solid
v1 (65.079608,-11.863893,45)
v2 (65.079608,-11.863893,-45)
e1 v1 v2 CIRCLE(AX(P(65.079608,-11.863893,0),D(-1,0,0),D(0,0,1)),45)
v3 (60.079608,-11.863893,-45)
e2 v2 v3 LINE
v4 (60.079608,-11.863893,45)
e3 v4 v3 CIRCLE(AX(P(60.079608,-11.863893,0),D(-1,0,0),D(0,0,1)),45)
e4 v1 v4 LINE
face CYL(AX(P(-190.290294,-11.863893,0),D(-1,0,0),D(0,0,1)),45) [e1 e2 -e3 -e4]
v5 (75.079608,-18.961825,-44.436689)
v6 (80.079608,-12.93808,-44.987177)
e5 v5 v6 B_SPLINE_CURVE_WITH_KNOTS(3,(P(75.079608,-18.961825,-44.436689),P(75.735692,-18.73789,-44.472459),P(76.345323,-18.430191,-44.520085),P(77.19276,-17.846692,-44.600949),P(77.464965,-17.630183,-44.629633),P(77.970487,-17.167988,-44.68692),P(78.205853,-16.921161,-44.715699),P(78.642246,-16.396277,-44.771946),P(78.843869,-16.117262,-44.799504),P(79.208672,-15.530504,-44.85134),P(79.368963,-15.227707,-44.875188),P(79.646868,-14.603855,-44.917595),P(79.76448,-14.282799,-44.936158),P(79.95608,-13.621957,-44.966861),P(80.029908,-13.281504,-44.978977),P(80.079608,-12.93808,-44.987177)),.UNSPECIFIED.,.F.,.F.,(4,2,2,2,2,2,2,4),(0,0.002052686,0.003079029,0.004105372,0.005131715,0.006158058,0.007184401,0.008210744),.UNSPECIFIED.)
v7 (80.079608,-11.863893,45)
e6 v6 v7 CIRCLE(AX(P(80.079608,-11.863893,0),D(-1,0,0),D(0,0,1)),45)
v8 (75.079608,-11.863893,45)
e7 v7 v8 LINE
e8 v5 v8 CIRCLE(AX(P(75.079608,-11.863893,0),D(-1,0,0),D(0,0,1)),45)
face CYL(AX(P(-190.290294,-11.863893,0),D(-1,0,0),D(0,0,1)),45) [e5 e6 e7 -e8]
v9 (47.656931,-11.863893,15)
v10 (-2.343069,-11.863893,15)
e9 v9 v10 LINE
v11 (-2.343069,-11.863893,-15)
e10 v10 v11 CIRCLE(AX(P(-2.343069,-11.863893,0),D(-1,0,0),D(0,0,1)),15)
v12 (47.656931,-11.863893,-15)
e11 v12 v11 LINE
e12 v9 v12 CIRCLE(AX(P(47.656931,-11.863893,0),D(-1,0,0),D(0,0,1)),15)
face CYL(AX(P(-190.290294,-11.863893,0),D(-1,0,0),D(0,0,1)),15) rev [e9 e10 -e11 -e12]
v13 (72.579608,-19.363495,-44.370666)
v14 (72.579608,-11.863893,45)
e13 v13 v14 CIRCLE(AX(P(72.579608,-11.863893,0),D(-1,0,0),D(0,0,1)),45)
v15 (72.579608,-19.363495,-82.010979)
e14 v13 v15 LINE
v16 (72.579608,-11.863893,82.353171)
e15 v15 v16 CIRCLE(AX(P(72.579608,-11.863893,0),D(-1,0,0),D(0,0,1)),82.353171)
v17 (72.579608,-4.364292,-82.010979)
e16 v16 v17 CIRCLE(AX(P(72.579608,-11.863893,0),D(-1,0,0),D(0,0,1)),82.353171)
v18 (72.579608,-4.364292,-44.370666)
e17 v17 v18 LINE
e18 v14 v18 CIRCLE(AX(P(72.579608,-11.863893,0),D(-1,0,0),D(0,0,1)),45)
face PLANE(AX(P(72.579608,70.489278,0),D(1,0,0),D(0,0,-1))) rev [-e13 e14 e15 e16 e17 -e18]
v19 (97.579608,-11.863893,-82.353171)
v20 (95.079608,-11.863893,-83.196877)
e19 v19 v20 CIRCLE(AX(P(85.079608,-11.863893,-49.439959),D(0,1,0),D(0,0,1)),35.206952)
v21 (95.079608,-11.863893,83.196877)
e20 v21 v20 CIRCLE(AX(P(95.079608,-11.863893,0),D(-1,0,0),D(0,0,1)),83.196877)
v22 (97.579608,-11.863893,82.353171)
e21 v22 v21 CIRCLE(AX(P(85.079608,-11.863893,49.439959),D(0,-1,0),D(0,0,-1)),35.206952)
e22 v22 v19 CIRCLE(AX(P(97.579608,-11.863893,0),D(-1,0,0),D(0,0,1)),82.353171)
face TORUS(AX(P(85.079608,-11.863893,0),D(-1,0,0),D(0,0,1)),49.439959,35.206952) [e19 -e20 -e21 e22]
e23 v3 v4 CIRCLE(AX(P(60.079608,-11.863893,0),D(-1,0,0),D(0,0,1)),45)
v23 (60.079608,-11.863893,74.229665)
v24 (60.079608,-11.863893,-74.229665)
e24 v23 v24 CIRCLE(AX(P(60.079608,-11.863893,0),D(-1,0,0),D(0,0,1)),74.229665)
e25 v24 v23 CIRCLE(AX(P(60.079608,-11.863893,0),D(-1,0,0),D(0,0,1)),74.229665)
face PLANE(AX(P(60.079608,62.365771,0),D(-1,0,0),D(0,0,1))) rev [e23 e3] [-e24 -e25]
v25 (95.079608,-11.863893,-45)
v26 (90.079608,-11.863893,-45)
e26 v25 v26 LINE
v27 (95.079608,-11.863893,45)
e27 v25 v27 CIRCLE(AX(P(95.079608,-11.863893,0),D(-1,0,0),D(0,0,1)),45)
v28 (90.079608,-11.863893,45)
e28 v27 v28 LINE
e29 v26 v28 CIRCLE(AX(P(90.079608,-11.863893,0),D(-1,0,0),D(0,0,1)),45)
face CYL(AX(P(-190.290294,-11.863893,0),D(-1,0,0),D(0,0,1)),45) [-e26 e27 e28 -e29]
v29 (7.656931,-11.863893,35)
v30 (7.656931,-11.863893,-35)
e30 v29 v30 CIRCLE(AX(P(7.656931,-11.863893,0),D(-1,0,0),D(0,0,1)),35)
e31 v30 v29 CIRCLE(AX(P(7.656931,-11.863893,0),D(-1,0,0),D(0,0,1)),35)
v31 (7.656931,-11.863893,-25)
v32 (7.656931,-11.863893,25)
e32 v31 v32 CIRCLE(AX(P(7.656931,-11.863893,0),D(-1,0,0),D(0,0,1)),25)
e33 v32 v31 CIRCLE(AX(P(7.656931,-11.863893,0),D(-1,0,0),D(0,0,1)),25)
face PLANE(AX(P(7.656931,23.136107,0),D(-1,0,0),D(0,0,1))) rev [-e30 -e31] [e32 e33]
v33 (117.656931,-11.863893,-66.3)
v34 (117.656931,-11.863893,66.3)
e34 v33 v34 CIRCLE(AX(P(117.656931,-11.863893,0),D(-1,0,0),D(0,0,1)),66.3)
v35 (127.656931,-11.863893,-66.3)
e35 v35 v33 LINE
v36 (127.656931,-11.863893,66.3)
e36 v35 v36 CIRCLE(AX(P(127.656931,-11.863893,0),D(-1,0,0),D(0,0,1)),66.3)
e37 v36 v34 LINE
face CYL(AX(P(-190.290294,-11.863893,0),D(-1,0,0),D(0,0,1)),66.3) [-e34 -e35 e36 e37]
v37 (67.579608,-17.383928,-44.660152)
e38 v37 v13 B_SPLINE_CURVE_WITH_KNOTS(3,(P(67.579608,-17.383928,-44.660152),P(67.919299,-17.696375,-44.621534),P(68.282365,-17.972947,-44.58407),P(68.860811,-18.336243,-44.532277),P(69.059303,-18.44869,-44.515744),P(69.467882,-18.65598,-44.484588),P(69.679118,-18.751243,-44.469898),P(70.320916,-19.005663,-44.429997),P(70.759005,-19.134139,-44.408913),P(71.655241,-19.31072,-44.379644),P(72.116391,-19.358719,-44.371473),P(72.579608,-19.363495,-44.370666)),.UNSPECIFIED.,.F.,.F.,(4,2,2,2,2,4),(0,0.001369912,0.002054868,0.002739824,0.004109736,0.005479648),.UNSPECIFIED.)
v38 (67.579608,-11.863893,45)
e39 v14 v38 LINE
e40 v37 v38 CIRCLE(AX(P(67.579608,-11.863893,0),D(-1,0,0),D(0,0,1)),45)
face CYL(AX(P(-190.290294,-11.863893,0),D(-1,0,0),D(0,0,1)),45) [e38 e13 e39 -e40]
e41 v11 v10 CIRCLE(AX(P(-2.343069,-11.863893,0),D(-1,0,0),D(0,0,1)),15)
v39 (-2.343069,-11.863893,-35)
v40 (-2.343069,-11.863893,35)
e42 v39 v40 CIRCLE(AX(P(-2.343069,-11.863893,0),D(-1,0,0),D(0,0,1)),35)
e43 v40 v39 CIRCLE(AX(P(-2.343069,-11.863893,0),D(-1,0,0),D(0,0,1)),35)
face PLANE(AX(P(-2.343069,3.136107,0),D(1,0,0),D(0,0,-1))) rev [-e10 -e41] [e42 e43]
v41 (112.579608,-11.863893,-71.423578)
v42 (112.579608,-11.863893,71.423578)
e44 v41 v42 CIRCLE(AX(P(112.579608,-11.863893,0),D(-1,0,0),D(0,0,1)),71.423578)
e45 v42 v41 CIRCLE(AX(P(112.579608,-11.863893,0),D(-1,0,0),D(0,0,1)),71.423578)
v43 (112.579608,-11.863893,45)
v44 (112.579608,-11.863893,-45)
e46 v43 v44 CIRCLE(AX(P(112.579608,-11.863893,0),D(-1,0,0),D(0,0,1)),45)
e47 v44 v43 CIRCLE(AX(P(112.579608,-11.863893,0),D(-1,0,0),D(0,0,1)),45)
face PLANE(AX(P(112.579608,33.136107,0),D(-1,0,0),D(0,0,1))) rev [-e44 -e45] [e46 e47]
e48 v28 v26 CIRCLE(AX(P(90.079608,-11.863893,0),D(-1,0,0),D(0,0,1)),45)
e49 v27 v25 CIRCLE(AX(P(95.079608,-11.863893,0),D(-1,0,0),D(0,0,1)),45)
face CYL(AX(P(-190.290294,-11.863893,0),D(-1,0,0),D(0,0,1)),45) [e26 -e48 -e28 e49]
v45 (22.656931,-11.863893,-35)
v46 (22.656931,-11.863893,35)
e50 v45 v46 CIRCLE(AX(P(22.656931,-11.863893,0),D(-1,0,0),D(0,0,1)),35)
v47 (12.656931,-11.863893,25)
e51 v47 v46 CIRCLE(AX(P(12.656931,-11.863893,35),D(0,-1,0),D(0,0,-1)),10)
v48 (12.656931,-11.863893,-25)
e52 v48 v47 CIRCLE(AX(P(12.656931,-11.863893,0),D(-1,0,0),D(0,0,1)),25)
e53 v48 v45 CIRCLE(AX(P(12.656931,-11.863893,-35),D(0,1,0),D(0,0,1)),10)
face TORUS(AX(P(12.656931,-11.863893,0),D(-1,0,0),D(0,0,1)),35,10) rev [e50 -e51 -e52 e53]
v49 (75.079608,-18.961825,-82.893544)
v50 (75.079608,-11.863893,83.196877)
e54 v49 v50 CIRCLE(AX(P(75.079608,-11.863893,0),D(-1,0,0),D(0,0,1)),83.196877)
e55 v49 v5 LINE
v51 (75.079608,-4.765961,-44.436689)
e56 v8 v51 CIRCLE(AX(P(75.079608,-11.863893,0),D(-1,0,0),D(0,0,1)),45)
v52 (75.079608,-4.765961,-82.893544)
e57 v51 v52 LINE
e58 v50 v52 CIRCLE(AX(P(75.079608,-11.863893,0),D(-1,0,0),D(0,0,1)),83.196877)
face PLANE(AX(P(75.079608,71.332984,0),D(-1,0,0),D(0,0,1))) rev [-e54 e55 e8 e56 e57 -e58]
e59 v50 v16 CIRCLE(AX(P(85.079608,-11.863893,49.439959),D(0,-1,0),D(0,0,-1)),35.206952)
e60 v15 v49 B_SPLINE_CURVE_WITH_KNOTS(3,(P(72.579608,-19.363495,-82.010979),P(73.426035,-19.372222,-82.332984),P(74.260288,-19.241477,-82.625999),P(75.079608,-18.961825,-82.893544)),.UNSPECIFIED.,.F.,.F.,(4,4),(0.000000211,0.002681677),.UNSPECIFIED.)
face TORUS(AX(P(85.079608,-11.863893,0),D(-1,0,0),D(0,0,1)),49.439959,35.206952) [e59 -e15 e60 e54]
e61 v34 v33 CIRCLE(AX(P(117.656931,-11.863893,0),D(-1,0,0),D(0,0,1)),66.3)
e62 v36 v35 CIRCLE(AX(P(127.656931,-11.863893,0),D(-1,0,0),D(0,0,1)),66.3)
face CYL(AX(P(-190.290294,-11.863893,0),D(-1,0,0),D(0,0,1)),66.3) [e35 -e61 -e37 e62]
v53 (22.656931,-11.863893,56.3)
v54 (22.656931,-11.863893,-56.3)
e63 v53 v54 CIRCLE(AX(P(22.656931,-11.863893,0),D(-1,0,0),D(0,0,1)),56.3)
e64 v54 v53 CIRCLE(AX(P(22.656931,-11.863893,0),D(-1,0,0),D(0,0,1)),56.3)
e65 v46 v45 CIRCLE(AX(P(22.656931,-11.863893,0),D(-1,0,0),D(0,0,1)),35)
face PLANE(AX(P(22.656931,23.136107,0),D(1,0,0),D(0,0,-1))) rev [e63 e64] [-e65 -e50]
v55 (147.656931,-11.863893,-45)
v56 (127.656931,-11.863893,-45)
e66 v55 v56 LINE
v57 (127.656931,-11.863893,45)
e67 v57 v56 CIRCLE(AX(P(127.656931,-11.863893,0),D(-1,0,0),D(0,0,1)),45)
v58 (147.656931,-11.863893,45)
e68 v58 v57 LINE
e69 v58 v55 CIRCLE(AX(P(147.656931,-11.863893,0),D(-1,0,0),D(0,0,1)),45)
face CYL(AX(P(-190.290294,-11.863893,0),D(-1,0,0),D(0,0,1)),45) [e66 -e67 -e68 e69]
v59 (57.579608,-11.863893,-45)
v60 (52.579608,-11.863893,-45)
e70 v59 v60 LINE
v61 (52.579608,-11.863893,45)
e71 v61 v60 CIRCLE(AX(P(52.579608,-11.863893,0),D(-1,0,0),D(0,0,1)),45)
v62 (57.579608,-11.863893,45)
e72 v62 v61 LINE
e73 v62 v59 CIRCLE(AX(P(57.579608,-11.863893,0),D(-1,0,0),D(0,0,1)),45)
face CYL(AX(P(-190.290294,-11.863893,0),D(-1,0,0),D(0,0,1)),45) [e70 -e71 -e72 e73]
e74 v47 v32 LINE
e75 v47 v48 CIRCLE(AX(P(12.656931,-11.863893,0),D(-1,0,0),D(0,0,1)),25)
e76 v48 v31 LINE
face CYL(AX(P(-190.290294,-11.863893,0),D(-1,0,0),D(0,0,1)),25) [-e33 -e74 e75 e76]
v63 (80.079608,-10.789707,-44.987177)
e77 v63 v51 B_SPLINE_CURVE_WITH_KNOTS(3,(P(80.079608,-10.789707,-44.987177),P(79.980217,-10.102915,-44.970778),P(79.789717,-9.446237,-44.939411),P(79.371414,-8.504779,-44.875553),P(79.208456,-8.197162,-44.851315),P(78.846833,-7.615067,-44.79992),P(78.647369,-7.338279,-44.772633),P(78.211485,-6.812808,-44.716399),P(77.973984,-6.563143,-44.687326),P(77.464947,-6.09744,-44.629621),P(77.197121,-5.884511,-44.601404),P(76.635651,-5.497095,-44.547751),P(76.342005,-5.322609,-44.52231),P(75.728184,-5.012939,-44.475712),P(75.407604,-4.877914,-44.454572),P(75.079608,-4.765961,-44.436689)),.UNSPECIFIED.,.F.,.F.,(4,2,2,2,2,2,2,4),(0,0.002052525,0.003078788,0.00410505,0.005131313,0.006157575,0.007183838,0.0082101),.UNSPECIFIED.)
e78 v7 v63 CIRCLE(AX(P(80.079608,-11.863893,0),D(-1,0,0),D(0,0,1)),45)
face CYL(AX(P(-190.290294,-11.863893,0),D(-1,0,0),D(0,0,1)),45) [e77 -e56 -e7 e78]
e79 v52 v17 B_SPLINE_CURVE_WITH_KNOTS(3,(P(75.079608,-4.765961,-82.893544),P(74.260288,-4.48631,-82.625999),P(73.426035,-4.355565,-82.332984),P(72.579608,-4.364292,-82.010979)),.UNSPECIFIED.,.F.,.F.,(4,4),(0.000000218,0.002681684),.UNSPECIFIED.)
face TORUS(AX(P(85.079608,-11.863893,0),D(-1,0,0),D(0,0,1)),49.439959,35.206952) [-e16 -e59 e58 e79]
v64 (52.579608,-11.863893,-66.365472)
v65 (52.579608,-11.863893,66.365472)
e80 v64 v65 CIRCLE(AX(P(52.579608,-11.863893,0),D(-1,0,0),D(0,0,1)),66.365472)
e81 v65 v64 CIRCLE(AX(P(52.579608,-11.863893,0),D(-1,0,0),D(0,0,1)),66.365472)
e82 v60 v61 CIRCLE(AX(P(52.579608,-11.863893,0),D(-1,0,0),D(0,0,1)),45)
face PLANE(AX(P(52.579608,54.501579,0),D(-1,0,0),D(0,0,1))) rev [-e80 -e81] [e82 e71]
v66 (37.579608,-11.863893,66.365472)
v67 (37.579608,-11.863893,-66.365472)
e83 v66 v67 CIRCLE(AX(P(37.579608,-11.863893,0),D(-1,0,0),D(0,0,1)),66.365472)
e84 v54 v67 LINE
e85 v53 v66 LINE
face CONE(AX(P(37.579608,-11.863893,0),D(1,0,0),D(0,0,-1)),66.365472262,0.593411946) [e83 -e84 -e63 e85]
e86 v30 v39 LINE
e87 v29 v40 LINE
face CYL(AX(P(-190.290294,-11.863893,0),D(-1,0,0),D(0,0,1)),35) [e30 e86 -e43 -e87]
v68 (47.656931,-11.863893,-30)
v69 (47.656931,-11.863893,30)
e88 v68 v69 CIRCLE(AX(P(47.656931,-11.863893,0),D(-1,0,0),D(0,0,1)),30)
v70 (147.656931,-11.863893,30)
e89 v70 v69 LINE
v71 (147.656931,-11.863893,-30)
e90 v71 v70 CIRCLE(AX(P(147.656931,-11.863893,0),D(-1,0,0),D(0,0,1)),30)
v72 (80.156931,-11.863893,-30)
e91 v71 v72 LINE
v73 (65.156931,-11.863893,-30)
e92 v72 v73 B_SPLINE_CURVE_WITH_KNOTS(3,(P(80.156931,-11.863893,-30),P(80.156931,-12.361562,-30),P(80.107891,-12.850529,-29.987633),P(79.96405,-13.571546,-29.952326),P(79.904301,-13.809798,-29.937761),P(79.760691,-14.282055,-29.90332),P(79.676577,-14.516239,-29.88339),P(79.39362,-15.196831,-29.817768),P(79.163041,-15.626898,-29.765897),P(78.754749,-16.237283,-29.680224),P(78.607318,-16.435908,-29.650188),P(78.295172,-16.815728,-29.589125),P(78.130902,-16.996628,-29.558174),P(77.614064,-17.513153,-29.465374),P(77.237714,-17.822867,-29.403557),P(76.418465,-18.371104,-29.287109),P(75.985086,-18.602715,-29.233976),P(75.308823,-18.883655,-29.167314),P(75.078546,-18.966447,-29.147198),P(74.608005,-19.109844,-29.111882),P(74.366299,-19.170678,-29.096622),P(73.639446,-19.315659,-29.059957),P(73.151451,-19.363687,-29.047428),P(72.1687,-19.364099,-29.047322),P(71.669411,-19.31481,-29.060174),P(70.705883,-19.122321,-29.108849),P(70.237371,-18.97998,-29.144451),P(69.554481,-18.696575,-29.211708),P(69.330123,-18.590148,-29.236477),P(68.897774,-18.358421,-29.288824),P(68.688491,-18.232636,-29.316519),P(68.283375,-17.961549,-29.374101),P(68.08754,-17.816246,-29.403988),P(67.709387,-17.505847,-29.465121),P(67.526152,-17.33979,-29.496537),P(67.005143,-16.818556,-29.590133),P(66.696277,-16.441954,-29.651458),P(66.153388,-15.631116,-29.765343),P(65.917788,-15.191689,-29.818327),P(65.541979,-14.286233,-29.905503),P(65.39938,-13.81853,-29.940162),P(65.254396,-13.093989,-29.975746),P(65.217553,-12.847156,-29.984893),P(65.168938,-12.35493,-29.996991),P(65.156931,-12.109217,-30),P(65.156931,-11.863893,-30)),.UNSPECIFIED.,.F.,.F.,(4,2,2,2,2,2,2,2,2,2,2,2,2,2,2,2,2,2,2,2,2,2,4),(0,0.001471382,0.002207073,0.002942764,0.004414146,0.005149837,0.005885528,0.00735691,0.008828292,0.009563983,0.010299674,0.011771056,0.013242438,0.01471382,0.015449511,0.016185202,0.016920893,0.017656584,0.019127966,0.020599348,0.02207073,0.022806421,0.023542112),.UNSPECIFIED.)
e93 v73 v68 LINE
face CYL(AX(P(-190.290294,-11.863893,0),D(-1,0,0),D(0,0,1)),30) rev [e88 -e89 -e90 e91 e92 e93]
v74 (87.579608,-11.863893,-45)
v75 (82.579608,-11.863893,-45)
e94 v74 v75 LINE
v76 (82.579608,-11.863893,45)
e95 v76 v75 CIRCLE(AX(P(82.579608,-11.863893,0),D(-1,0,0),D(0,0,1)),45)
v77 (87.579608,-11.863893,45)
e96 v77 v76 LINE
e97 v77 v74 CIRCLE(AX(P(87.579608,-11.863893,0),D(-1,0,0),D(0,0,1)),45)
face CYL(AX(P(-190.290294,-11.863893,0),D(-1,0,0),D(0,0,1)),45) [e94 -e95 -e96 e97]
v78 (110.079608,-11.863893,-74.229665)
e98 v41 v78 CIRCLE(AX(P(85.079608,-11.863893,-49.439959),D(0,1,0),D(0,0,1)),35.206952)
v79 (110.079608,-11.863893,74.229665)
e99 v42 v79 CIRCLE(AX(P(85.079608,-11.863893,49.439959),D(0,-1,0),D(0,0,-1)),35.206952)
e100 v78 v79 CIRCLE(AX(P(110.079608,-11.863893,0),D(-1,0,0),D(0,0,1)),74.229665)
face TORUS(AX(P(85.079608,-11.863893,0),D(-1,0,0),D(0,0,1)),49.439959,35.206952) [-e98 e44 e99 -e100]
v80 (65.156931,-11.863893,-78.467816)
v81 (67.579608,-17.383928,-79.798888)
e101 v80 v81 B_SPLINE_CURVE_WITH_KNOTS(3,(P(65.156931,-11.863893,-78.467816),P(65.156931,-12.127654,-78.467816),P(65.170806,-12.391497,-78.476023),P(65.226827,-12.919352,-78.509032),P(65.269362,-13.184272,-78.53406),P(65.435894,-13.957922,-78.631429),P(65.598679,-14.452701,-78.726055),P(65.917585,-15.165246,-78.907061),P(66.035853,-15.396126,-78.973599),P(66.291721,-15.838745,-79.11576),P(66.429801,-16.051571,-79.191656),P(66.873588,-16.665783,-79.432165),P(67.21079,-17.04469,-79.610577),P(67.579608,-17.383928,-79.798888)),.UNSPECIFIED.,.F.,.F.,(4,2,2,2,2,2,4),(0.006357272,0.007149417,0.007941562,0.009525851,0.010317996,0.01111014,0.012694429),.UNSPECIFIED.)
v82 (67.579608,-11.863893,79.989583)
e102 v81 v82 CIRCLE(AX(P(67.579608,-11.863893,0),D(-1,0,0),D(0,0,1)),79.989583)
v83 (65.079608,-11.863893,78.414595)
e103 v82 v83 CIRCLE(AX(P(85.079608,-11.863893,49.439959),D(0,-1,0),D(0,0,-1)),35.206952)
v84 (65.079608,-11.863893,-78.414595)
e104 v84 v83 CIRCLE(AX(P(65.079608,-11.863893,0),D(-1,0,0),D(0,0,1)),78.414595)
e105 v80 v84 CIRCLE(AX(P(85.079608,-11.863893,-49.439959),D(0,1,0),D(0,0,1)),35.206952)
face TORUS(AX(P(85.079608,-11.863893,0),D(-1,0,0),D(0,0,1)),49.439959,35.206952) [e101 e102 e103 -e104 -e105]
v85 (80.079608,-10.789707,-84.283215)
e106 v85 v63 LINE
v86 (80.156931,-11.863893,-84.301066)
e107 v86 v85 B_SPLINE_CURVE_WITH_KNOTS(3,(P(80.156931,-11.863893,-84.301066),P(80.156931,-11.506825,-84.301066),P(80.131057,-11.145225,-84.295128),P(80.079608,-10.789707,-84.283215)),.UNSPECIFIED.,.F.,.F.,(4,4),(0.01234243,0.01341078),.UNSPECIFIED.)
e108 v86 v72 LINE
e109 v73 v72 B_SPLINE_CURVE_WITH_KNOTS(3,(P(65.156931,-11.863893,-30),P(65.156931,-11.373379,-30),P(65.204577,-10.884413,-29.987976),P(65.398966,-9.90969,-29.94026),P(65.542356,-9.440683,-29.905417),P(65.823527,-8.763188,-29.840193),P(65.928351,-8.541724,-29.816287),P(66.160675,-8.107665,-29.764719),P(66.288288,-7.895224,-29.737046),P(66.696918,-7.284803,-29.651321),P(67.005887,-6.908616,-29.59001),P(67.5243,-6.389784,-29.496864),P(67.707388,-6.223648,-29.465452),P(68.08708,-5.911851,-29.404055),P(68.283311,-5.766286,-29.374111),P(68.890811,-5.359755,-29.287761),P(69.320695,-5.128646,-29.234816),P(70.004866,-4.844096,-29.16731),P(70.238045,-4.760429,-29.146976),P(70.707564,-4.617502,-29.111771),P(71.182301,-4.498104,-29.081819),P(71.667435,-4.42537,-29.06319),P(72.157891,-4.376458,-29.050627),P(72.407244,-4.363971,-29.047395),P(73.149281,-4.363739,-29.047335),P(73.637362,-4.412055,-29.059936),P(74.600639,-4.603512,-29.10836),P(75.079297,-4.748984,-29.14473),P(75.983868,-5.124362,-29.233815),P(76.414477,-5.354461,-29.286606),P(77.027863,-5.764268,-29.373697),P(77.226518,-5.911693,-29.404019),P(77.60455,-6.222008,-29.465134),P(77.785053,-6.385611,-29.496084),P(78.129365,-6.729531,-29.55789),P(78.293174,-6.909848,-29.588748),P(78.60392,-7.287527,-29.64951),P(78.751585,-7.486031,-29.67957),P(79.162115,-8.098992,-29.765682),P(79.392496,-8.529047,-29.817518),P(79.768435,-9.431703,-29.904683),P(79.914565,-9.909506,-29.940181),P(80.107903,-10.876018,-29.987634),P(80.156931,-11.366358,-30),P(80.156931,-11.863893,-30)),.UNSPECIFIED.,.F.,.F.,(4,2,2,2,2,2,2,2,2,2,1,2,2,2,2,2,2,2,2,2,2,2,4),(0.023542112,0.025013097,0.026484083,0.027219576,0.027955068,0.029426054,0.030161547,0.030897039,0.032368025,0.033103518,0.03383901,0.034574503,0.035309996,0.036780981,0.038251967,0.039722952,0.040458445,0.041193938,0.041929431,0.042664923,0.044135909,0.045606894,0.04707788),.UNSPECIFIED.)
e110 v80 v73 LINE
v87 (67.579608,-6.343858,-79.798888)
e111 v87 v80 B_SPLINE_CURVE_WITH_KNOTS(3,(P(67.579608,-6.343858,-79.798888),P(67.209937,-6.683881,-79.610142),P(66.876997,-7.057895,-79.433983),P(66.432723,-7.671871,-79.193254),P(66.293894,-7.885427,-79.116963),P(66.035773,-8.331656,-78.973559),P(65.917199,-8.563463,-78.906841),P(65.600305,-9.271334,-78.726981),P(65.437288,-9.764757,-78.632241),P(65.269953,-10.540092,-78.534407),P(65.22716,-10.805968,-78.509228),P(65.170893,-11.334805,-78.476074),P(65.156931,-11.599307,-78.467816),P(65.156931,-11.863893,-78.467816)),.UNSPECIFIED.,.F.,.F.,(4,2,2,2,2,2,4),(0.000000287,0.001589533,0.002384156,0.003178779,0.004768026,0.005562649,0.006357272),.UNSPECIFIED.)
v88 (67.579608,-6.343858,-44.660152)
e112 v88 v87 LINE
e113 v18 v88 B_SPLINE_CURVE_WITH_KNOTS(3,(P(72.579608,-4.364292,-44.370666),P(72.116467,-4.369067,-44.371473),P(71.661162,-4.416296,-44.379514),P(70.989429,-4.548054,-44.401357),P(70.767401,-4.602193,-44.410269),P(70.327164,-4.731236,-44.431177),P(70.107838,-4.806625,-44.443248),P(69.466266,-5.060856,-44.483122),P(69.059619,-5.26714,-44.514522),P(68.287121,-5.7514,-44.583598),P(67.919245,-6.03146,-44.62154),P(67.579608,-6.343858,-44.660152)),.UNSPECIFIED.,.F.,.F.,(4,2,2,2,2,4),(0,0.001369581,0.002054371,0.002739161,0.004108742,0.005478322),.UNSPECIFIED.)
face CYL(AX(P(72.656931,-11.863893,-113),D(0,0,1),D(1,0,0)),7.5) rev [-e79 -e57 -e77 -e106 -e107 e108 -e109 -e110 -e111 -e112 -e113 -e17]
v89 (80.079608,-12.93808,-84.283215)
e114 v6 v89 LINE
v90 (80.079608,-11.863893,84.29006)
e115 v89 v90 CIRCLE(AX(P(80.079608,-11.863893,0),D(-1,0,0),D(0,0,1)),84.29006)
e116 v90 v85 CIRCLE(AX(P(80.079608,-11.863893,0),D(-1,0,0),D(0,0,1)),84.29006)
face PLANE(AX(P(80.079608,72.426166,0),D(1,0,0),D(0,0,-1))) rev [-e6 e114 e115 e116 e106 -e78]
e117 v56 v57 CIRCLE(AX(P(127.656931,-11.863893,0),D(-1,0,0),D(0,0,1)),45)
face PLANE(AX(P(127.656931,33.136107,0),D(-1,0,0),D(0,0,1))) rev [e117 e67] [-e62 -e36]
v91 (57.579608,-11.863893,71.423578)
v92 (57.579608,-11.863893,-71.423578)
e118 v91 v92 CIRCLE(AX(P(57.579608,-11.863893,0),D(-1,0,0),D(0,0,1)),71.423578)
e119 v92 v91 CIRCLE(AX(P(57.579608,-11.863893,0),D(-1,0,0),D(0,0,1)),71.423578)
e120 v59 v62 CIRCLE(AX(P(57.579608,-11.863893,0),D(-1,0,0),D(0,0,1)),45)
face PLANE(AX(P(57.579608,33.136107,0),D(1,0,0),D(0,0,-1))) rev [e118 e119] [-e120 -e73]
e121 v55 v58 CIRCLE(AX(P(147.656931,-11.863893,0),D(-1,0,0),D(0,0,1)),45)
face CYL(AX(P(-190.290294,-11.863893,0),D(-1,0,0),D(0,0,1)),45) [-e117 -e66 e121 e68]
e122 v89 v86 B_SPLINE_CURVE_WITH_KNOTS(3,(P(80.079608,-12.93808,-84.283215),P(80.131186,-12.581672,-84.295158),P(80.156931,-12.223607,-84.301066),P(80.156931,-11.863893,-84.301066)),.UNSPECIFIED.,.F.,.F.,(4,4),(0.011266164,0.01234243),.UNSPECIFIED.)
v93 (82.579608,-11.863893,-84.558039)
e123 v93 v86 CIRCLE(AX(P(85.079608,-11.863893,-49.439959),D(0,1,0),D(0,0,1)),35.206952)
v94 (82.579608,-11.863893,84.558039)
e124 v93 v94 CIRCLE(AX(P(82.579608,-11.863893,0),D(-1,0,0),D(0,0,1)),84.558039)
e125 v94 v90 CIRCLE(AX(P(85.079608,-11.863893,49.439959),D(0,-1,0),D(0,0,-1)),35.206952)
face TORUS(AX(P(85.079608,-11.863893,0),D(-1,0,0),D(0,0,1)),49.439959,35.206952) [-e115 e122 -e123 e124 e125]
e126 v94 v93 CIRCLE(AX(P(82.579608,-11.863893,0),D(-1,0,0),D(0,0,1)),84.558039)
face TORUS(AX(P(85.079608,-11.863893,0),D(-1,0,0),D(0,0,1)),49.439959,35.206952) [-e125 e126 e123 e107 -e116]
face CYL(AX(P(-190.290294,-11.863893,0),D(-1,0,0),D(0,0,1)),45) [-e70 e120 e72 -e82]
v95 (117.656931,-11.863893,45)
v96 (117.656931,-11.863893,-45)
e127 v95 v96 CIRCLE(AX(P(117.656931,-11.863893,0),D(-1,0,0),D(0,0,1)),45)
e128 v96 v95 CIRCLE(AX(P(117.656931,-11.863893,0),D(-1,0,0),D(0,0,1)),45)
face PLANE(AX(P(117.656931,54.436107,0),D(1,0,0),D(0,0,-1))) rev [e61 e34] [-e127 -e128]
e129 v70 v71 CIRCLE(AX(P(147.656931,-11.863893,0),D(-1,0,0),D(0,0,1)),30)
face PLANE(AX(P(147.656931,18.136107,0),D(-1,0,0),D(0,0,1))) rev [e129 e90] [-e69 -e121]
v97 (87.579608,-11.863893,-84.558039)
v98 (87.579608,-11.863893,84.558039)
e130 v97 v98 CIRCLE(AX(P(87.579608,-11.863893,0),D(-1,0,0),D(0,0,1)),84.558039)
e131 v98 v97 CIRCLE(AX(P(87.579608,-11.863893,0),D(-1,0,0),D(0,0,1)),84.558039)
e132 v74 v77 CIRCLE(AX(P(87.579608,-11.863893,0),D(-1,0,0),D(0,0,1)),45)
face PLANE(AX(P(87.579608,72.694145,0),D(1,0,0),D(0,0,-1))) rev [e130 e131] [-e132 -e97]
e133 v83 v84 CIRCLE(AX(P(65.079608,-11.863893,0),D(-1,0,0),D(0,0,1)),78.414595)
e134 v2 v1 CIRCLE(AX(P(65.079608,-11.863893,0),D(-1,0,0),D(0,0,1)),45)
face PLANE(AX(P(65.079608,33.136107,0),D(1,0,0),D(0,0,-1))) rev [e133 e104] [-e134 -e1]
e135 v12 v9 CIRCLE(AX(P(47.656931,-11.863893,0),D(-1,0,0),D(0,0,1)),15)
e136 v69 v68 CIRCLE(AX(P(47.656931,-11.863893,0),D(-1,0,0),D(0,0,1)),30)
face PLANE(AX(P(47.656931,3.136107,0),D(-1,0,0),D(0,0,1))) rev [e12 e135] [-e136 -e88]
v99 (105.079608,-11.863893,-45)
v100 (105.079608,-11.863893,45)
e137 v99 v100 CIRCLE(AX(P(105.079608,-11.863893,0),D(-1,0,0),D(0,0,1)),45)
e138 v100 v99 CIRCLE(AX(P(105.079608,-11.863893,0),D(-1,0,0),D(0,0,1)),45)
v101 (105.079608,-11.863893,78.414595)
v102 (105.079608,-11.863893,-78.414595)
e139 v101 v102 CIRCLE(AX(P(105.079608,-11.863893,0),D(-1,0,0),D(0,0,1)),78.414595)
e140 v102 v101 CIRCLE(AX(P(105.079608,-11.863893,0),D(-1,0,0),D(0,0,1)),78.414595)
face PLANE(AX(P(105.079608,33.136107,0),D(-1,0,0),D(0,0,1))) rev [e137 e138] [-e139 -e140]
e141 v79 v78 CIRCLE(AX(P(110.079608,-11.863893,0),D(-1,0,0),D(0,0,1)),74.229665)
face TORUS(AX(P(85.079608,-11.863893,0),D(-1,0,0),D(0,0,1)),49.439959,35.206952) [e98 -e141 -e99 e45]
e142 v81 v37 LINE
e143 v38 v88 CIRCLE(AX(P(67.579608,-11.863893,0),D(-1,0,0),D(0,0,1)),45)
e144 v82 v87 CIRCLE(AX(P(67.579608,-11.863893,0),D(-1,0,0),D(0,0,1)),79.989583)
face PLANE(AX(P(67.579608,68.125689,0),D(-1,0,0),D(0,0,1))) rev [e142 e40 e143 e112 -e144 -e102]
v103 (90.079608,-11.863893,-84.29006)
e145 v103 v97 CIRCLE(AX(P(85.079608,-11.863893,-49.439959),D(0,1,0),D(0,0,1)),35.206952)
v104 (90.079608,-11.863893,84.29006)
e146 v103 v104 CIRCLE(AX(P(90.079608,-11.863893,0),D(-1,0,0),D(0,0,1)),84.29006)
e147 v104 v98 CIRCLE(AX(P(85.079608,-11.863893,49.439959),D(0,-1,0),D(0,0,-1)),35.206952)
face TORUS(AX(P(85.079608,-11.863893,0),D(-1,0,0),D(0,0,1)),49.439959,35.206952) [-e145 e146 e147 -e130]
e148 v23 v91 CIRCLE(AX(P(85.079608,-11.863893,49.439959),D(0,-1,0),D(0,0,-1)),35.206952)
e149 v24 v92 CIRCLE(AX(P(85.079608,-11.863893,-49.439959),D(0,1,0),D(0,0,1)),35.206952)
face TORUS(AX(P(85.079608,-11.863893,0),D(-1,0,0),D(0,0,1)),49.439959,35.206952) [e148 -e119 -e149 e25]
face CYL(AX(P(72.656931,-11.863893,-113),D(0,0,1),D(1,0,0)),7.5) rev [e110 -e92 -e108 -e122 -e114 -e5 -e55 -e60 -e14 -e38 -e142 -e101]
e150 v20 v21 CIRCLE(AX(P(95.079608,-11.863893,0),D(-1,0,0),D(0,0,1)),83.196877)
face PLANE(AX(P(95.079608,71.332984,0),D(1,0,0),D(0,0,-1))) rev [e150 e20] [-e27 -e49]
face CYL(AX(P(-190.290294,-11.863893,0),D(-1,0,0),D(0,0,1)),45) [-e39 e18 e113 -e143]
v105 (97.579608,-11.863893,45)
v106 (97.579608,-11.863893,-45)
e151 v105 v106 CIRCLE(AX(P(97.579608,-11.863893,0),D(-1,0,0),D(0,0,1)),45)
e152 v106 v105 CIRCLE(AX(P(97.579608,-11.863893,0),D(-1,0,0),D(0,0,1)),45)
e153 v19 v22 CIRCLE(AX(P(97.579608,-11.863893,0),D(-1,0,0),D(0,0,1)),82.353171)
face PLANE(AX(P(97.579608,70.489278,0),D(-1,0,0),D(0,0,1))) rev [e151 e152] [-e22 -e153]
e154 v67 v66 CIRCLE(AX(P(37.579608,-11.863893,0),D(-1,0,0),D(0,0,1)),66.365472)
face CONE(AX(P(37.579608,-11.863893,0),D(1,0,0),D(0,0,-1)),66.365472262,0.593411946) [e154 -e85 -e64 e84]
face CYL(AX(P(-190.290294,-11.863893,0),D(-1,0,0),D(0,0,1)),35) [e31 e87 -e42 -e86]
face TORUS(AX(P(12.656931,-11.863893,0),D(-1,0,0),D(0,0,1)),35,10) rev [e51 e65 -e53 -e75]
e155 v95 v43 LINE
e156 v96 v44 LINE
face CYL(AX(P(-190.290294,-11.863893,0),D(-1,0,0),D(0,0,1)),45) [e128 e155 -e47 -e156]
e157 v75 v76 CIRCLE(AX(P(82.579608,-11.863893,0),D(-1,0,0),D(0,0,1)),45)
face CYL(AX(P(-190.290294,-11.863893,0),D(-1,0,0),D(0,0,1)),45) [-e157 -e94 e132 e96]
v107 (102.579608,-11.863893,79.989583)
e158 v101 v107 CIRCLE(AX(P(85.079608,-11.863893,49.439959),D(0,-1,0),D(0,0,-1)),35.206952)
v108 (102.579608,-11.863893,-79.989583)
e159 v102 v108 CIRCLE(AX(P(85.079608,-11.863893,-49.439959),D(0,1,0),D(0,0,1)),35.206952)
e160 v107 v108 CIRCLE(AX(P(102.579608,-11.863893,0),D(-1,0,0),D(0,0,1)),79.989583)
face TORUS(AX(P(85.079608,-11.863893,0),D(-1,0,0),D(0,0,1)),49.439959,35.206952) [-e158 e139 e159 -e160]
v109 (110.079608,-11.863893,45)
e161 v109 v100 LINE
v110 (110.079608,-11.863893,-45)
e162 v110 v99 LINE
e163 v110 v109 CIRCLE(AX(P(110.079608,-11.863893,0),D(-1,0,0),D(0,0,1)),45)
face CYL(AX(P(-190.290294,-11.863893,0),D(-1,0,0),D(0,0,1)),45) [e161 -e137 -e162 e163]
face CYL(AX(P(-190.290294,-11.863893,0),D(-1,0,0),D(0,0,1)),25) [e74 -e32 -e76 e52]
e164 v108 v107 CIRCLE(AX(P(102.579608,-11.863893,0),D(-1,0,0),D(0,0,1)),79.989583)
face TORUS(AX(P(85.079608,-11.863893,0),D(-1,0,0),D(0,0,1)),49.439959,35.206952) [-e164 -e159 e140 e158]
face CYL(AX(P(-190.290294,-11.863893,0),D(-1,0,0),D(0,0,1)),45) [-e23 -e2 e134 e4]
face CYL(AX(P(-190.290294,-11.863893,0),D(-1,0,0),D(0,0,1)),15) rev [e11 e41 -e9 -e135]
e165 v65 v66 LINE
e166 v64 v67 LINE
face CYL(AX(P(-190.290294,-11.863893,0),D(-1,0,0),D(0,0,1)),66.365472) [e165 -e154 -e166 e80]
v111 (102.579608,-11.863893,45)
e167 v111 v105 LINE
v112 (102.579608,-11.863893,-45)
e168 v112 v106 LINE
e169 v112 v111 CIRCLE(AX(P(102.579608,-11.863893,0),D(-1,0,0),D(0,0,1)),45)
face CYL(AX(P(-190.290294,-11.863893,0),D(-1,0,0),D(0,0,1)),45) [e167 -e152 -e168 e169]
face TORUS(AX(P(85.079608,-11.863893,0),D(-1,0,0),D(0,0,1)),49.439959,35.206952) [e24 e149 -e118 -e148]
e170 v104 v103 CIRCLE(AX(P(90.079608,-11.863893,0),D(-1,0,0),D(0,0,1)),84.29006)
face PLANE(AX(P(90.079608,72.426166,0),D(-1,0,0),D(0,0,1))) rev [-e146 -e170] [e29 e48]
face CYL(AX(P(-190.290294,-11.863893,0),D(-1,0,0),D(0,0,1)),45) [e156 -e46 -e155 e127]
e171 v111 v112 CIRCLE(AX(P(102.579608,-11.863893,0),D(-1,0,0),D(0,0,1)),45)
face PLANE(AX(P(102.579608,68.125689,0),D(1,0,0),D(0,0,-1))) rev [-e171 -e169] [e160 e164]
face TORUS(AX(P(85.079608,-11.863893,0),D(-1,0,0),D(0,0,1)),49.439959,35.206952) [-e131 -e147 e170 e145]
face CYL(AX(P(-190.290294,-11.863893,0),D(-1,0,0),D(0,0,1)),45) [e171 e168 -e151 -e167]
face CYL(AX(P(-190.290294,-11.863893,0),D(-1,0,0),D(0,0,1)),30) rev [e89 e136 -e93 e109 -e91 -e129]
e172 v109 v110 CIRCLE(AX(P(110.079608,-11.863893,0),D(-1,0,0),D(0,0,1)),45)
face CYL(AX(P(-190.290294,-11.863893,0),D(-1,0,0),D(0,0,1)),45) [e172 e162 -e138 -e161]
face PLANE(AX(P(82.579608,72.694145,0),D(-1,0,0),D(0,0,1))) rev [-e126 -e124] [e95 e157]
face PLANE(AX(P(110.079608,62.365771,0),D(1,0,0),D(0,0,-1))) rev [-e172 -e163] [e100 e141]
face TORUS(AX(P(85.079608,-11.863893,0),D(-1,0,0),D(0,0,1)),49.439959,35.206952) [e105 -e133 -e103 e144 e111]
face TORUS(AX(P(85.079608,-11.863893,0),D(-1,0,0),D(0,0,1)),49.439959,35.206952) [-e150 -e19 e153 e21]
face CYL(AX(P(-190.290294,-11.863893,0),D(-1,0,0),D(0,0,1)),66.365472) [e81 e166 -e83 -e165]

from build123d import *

# Parameters (mm, degrees)
THROUGH_BORE_PROFILE_R = 7.5
THROUGH_BORE_DEPTH     = 113


with BuildPart() as part:
    # Finned Body Profile → Finned Body Revolve (revolve)
    with BuildSketch(Plane.XY, mode=Mode.PRIVATE) as finned_body_revolve_sk:
        with BuildLine():
            Line((-2.343068637, 3.136106772), (-2.343068637, 23.136106772))
            Line((-2.343068637, 23.136106772), (7.656931363, 23.136106772))
            Line((7.656931363, 23.136106772), (7.656931363, 13.136106772))
            Line((7.656931363, 13.136106772), (12.656931363, 13.136106772))
            ThreePointArc((12.656931363, 13.136106772), (19.727999175, 16.06503896), (22.656931363, 23.136106772))
            Line((22.656931363, 23.136106772), (22.656931363, 44.436106772))
            Line((22.656931363, 44.436106772), (37.579607669, 54.501579034))
            Line((37.579607669, 54.501579034), (52.579607669, 54.501579034))
            Line((52.579607669, 54.501579034), (52.579607669, 33.136106772))
            Line((52.579607669, 33.136106772), (57.579607669, 33.136106772))
            Line((57.579607669, 33.136106772), (57.579607669, 59.559684826))
            ThreePointArc((57.579607669, 59.559684826), (58.792138591, 60.9961101), (60.079607669, 62.365771438))
            Line((60.079607669, 62.365771438), (60.079607669, 33.136106772))
            Line((60.079607669, 33.136106772), (65.079607669, 33.136106772))
            Line((65.079607669, 33.136106772), (65.079607669, 66.550701361))
            ThreePointArc((65.079607669, 66.550701361), (66.313077705, 67.364433648), (67.579607669, 68.125689463))
            Line((67.579607669, 68.125689463), (67.579607669, 33.136106772))
            Line((67.579607669, 33.136106772), (72.579607669, 33.136106772))
            Line((72.579607669, 33.136106772), (72.579607669, 70.489277526))
            ThreePointArc((72.579607669, 70.489277526), (73.821701113, 70.934558663), (75.079607669, 71.332983701))
            Line((75.079607669, 71.332983701), (75.079607669, 33.136106772))
            Line((75.079607669, 33.136106772), (80.079607669, 33.136106772))
            Line((80.079607669, 33.136106772), (80.079607669, 72.426166319))
            ThreePointArc((80.079607669, 72.426166319), (81.327214675, 72.582480256), (82.579607669, 72.694145278))
            Line((82.579607669, 72.694145278), (82.579607669, 33.136106772))
            Line((82.579607669, 33.136106772), (87.579607669, 33.136106772))
            Line((87.579607669, 33.136106772), (87.579607669, 72.694145278))
            ThreePointArc((87.579607669, 72.694145278), (88.832000663, 72.582480256), (90.079607669, 72.426166319))
            Line((90.079607669, 72.426166319), (90.079607669, 33.136106772))
            Line((90.079607669, 33.136106772), (95.079607669, 33.136106772))
            Line((95.079607669, 33.136106772), (95.079607669, 71.332983701))
            ThreePointArc((95.079607669, 71.332983701), (96.337514225, 70.934558663), (97.579607669, 70.489277526))
            Line((97.579607669, 70.489277526), (97.579607669, 33.136106772))
            Line((97.579607669, 33.136106772), (102.579607669, 33.136106772))
            Line((102.579607669, 33.136106772), (102.579607669, 68.125689463))
            ThreePointArc((102.579607669, 68.125689463), (103.846137633, 67.364433648), (105.079607669, 66.550701361))
            Line((105.079607669, 66.550701361), (105.079607669, 33.136106772))
            Line((105.079607669, 33.136106772), (110.079607669, 33.136106772))
            Line((110.079607669, 33.136106772), (110.079607669, 62.365771438))
            ThreePointArc((110.079607669, 62.365771438), (111.367076747, 60.9961101), (112.579607669, 59.559684826))
            Line((112.579607669, 59.559684826), (112.579607669, 33.136106772))
            Line((112.579607669, 33.136106772), (117.656931363, 33.136106772))
            Line((117.656931363, 33.136106772), (117.656931363, 54.436106772))
            Line((117.656931363, 54.436106772), (127.656931363, 54.436106772))
            Line((127.656931363, 54.436106772), (127.656931363, 33.136106772))
            Line((127.656931363, 33.136106772), (147.656931363, 33.136106772))
            Line((147.656931363, 33.136106772), (147.656931363, 18.136106772))
            Line((147.656931363, 18.136106772), (47.656931363, 18.136106772))
            Line((47.656931363, 18.136106772), (47.656931363, 3.136106772))
            Line((47.656931363, 3.136106772), (-2.343068637, 3.136106772))
        make_face()
    revolve(finned_body_revolve_sk.sketch.rotate(Axis((-190.290293796, -11.863893228, 0), (1, 0, 0)), 90), axis=Axis((-190.290293796, -11.863893228, 0), (1, 0, 0)))

    # Through Bore Profile → Through Bore (cut)
    with BuildSketch(Plane.XY):
        with Locations((72.656931363, -11.863893228)):
            Circle(THROUGH_BORE_PROFILE_R)
    extrude(amount=-THROUGH_BORE_DEPTH, mode=Mode.SUBTRACT)


solid = part.part
